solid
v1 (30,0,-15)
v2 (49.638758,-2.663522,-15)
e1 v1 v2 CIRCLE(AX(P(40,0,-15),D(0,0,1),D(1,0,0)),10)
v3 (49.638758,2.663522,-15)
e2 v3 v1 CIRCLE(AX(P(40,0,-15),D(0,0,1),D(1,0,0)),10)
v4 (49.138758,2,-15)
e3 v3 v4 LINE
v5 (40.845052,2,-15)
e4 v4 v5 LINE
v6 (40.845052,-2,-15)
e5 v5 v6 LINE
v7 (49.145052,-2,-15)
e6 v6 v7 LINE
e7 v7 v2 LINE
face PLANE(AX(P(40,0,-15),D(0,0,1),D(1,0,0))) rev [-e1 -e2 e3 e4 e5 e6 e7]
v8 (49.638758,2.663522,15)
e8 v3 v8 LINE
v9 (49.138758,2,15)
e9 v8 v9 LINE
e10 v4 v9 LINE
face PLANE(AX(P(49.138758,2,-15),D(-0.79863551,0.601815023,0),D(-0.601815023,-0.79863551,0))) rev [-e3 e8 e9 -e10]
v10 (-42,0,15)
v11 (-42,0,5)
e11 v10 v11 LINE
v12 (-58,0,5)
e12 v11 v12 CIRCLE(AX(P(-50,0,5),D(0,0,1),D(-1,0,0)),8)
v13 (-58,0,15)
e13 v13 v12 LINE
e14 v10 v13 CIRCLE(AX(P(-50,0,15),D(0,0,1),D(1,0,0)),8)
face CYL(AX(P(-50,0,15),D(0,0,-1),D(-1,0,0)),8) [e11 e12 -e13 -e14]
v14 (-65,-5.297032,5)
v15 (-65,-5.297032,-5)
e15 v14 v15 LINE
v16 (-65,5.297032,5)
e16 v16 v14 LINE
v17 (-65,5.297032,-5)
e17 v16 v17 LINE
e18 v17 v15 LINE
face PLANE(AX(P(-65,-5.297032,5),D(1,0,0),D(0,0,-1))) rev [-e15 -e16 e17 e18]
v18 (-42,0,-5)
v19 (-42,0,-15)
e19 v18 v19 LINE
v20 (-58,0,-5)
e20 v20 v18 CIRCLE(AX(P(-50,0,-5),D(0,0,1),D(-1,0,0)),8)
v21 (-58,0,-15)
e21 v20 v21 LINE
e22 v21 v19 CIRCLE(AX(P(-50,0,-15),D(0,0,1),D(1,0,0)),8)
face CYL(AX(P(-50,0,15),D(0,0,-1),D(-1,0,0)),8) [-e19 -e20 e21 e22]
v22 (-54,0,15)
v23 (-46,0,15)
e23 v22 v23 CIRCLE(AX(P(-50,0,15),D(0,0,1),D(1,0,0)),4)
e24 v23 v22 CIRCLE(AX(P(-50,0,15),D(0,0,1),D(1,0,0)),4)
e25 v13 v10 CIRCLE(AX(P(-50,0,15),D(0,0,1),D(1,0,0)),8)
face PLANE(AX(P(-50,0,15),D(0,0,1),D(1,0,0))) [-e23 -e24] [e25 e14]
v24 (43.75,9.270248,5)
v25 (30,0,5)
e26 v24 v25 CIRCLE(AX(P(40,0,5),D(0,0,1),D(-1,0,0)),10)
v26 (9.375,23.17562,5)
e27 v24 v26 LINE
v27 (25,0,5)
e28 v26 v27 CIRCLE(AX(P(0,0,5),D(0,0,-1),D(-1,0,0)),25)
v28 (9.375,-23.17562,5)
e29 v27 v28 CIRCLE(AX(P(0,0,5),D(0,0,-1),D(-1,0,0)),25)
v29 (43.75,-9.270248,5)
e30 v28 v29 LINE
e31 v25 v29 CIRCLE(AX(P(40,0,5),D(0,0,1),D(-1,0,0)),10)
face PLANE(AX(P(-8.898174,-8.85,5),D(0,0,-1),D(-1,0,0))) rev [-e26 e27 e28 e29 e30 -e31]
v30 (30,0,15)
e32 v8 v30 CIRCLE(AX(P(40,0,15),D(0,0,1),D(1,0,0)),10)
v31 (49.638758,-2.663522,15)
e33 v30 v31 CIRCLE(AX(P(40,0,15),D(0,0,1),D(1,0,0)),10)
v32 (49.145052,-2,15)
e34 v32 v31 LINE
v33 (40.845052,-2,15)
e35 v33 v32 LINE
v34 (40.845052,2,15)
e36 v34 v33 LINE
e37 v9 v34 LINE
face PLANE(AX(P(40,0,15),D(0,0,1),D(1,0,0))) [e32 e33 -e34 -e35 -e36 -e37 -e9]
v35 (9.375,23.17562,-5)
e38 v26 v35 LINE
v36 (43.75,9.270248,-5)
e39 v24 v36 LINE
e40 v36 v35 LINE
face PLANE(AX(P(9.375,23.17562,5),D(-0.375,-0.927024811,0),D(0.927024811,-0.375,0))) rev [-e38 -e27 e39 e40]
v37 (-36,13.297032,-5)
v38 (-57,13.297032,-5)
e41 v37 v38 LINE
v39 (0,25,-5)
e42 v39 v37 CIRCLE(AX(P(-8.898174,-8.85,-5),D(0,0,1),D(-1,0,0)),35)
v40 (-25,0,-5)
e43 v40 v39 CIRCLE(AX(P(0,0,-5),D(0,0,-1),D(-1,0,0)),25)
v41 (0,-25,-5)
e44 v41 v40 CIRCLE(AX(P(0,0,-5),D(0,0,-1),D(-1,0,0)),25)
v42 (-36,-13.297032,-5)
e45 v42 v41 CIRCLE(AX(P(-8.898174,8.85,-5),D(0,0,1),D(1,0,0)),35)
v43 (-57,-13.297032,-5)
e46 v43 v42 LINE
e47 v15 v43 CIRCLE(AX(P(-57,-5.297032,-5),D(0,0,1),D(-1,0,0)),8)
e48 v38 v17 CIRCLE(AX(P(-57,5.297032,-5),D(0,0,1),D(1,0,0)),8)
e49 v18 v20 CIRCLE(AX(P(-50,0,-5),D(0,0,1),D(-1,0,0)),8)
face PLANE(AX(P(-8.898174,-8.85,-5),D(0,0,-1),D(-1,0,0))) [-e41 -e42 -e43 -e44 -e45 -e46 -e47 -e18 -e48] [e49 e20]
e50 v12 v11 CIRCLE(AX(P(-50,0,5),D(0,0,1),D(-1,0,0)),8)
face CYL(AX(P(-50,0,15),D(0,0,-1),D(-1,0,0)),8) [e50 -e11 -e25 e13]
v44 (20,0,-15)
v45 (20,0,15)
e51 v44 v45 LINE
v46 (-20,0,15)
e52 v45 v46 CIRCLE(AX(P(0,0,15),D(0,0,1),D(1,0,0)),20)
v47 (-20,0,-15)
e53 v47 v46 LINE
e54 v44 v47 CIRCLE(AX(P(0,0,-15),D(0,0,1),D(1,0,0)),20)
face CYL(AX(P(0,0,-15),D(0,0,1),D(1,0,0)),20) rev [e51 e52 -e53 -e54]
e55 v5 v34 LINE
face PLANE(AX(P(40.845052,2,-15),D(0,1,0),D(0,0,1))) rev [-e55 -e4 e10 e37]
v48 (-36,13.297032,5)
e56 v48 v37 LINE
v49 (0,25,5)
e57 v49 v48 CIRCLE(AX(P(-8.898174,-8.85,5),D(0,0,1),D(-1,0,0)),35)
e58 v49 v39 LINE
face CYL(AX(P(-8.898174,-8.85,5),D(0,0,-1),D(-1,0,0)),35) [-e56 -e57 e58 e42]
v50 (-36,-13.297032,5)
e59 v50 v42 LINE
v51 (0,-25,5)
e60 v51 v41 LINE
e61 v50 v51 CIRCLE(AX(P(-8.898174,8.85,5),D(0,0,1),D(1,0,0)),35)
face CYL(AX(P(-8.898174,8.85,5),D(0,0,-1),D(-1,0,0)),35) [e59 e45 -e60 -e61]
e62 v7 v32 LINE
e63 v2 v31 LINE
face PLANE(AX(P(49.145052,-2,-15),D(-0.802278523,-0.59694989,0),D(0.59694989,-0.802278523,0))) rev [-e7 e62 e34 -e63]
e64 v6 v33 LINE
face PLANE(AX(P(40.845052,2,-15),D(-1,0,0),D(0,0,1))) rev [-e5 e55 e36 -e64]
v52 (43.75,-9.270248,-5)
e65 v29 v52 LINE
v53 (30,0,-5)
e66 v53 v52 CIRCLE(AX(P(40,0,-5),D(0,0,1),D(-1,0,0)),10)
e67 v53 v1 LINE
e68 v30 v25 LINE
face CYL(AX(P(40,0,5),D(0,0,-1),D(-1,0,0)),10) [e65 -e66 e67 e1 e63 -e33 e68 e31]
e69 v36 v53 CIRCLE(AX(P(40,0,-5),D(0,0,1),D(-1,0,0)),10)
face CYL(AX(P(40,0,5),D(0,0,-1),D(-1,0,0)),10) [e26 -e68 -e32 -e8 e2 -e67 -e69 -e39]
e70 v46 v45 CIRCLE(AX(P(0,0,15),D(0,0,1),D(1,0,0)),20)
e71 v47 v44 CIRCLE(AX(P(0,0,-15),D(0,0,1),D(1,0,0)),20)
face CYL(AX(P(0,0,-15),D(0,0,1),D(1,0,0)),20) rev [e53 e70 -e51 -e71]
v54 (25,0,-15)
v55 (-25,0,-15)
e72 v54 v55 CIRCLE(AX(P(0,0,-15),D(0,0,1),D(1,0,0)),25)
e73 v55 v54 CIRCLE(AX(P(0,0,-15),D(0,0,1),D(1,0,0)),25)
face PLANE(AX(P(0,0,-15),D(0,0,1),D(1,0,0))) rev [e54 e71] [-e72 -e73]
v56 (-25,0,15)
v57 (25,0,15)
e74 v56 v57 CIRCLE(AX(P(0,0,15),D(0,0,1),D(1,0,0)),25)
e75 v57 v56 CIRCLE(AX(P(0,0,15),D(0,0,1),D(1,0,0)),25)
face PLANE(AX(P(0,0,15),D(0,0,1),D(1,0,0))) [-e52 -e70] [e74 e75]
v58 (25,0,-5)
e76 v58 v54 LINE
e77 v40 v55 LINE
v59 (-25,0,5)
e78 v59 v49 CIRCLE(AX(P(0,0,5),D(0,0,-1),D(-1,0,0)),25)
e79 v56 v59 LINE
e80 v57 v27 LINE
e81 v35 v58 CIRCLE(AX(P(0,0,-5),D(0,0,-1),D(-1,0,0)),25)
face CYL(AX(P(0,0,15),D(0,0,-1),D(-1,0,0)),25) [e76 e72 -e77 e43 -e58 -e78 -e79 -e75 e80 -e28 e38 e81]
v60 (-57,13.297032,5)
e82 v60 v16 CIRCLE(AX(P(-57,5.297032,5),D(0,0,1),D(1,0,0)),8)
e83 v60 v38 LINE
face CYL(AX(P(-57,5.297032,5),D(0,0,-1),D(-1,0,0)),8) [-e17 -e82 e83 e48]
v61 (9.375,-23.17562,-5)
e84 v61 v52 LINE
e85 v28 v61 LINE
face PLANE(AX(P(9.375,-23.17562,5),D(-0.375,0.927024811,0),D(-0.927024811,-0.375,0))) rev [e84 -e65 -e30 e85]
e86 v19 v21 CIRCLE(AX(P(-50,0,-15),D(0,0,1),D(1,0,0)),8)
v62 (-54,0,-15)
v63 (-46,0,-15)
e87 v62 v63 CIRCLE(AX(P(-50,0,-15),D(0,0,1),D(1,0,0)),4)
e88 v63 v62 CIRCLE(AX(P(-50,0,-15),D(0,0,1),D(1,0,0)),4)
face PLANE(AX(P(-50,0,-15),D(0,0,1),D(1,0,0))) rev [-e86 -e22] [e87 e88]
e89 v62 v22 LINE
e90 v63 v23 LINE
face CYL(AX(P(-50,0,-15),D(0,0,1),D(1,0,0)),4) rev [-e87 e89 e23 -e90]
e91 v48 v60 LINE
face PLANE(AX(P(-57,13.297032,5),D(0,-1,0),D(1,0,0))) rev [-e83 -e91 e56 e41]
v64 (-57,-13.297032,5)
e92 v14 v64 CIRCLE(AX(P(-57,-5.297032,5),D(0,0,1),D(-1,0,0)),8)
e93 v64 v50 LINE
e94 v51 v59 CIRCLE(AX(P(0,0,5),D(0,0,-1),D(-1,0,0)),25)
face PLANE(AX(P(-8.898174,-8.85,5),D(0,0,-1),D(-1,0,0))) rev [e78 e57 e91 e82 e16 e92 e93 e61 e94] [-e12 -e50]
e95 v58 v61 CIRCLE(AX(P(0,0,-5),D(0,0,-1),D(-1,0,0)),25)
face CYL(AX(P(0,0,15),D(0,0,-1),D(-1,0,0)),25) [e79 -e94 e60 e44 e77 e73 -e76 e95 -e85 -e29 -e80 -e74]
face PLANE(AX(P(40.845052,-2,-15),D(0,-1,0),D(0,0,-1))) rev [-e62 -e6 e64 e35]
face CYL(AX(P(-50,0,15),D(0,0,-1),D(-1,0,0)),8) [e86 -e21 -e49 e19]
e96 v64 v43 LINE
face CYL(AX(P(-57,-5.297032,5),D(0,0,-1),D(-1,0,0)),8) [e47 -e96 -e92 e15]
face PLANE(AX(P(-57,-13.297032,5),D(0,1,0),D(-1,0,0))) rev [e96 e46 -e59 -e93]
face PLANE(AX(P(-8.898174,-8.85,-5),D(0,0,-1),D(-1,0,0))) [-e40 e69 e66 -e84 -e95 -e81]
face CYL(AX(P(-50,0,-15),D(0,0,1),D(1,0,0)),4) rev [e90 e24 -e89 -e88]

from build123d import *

# Parameters (mm, degrees)
COLLAR_BODY_SKETCH_R   = 25
COLLAR_BODY_DEPTH      = 15
COLLAR_BODY_SKETCH_R_2 = 8
COLLAR_BODY_2_DEPTH    = 15
COLLAR_BODY_SKETCH_R_3 = 10
COLLAR_BODY_3_DEPTH    = 15
LINK_LUGS_DEPTH        = 5
CLAMP_SLOT_SKETCH_R    = 20
CLAMP_SLOT_SKETCH_R_2  = 4
CLAMP_SLOT_CUT_DEPTH   = 77.215631599


with BuildPart() as part:
    # Collar Body Sketch → Collar Body (new, symmetric)
    with BuildSketch(Plane.XY):
        Circle(COLLAR_BODY_SKETCH_R)
    extrude(amount=COLLAR_BODY_DEPTH, both=True)



with BuildPart() as body_2:
    # Collar Body Sketch → Collar Body 2 (new, symmetric)
    with BuildSketch(Plane.XY):
        with Locations((-50, 0)):
            Circle(COLLAR_BODY_SKETCH_R_2)
    extrude(amount=COLLAR_BODY_2_DEPTH, both=True)


with BuildPart() as body_3:
    # Collar Body Sketch → Collar Body 3 (new, symmetric)
    with BuildSketch(Plane.XY):
        with Locations((40, 0)):
            Circle(COLLAR_BODY_SKETCH_R_3)
    extrude(amount=COLLAR_BODY_3_DEPTH, both=True)


with BuildPart() as part_1:
    add(part.part)

    add(body_2.part)  # Link Lugs merges body 2

    add(body_3.part)  # Link Lugs merges body 3
    # Link Lugs Sketch → Link Lugs (add, symmetric)
    with BuildSketch(Plane.XY):
        with BuildLine():
            Line((-65, -5.297031987), (-65, 5.297031987))
            ThreePointArc((-65, 5.297031987), (-62.656854249, 10.953886237), (-57, 13.297031987))
            Line((-57, 13.297031987), (-36, 13.297031987))
            ThreePointArc((-36, 13.297031987), (-19.718668513, 24.43538565), (0, 25))
            ThreePointArc((0, 25), (4.775431561, 24.539666937), (9.375, 23.175620272))
            Line((9.375, 23.175620272), (43.75, 9.270248109))
            ThreePointArc((43.75, 9.270248109), (50, 0), (43.75, -9.270248109))
            Line((43.75, -9.270248109), (9.375, -23.175620272))
            ThreePointArc((9.375, -23.175620272), (4.775431561, -24.539666937), (0, -25))
            ThreePointArc((0, -25), (-19.718668513, -24.43538565), (-36, -13.297031987))
            Line((-36, -13.297031987), (-57, -13.297031987))
            ThreePointArc((-57, -13.297031987), (-62.656854249, -10.953886237), (-65, -5.297031987))
        make_face()
    extrude(amount=LINK_LUGS_DEPTH, both=True)

    # Clamp Slot Sketch → Clamp Slot Cut (cut, through all)
    with BuildSketch(Plane.XY.offset(15)):
        Circle(CLAMP_SLOT_SKETCH_R)
        with Locations((-50, 0)):
            Circle(CLAMP_SLOT_SKETCH_R_2)
        with BuildLine():
            Line((40.845051729, 2), (40.845051729, -2))
            Line((40.845051729, -2), (49.145051729, -2))
            Line((49.145051729, -2), (49.638757615, -2.663522411))
            ThreePointArc((49.638757615, -2.663522411), (50, 0), (49.638757615, 2.663522411))
            Line((49.638757615, 2.663522411), (49.138757615, 2))
            Line((49.138757615, 2), (40.845051729, 2))
        make_face()
    extrude(amount=-CLAMP_SLOT_CUT_DEPTH, mode=Mode.SUBTRACT)


solid = part_1.part
